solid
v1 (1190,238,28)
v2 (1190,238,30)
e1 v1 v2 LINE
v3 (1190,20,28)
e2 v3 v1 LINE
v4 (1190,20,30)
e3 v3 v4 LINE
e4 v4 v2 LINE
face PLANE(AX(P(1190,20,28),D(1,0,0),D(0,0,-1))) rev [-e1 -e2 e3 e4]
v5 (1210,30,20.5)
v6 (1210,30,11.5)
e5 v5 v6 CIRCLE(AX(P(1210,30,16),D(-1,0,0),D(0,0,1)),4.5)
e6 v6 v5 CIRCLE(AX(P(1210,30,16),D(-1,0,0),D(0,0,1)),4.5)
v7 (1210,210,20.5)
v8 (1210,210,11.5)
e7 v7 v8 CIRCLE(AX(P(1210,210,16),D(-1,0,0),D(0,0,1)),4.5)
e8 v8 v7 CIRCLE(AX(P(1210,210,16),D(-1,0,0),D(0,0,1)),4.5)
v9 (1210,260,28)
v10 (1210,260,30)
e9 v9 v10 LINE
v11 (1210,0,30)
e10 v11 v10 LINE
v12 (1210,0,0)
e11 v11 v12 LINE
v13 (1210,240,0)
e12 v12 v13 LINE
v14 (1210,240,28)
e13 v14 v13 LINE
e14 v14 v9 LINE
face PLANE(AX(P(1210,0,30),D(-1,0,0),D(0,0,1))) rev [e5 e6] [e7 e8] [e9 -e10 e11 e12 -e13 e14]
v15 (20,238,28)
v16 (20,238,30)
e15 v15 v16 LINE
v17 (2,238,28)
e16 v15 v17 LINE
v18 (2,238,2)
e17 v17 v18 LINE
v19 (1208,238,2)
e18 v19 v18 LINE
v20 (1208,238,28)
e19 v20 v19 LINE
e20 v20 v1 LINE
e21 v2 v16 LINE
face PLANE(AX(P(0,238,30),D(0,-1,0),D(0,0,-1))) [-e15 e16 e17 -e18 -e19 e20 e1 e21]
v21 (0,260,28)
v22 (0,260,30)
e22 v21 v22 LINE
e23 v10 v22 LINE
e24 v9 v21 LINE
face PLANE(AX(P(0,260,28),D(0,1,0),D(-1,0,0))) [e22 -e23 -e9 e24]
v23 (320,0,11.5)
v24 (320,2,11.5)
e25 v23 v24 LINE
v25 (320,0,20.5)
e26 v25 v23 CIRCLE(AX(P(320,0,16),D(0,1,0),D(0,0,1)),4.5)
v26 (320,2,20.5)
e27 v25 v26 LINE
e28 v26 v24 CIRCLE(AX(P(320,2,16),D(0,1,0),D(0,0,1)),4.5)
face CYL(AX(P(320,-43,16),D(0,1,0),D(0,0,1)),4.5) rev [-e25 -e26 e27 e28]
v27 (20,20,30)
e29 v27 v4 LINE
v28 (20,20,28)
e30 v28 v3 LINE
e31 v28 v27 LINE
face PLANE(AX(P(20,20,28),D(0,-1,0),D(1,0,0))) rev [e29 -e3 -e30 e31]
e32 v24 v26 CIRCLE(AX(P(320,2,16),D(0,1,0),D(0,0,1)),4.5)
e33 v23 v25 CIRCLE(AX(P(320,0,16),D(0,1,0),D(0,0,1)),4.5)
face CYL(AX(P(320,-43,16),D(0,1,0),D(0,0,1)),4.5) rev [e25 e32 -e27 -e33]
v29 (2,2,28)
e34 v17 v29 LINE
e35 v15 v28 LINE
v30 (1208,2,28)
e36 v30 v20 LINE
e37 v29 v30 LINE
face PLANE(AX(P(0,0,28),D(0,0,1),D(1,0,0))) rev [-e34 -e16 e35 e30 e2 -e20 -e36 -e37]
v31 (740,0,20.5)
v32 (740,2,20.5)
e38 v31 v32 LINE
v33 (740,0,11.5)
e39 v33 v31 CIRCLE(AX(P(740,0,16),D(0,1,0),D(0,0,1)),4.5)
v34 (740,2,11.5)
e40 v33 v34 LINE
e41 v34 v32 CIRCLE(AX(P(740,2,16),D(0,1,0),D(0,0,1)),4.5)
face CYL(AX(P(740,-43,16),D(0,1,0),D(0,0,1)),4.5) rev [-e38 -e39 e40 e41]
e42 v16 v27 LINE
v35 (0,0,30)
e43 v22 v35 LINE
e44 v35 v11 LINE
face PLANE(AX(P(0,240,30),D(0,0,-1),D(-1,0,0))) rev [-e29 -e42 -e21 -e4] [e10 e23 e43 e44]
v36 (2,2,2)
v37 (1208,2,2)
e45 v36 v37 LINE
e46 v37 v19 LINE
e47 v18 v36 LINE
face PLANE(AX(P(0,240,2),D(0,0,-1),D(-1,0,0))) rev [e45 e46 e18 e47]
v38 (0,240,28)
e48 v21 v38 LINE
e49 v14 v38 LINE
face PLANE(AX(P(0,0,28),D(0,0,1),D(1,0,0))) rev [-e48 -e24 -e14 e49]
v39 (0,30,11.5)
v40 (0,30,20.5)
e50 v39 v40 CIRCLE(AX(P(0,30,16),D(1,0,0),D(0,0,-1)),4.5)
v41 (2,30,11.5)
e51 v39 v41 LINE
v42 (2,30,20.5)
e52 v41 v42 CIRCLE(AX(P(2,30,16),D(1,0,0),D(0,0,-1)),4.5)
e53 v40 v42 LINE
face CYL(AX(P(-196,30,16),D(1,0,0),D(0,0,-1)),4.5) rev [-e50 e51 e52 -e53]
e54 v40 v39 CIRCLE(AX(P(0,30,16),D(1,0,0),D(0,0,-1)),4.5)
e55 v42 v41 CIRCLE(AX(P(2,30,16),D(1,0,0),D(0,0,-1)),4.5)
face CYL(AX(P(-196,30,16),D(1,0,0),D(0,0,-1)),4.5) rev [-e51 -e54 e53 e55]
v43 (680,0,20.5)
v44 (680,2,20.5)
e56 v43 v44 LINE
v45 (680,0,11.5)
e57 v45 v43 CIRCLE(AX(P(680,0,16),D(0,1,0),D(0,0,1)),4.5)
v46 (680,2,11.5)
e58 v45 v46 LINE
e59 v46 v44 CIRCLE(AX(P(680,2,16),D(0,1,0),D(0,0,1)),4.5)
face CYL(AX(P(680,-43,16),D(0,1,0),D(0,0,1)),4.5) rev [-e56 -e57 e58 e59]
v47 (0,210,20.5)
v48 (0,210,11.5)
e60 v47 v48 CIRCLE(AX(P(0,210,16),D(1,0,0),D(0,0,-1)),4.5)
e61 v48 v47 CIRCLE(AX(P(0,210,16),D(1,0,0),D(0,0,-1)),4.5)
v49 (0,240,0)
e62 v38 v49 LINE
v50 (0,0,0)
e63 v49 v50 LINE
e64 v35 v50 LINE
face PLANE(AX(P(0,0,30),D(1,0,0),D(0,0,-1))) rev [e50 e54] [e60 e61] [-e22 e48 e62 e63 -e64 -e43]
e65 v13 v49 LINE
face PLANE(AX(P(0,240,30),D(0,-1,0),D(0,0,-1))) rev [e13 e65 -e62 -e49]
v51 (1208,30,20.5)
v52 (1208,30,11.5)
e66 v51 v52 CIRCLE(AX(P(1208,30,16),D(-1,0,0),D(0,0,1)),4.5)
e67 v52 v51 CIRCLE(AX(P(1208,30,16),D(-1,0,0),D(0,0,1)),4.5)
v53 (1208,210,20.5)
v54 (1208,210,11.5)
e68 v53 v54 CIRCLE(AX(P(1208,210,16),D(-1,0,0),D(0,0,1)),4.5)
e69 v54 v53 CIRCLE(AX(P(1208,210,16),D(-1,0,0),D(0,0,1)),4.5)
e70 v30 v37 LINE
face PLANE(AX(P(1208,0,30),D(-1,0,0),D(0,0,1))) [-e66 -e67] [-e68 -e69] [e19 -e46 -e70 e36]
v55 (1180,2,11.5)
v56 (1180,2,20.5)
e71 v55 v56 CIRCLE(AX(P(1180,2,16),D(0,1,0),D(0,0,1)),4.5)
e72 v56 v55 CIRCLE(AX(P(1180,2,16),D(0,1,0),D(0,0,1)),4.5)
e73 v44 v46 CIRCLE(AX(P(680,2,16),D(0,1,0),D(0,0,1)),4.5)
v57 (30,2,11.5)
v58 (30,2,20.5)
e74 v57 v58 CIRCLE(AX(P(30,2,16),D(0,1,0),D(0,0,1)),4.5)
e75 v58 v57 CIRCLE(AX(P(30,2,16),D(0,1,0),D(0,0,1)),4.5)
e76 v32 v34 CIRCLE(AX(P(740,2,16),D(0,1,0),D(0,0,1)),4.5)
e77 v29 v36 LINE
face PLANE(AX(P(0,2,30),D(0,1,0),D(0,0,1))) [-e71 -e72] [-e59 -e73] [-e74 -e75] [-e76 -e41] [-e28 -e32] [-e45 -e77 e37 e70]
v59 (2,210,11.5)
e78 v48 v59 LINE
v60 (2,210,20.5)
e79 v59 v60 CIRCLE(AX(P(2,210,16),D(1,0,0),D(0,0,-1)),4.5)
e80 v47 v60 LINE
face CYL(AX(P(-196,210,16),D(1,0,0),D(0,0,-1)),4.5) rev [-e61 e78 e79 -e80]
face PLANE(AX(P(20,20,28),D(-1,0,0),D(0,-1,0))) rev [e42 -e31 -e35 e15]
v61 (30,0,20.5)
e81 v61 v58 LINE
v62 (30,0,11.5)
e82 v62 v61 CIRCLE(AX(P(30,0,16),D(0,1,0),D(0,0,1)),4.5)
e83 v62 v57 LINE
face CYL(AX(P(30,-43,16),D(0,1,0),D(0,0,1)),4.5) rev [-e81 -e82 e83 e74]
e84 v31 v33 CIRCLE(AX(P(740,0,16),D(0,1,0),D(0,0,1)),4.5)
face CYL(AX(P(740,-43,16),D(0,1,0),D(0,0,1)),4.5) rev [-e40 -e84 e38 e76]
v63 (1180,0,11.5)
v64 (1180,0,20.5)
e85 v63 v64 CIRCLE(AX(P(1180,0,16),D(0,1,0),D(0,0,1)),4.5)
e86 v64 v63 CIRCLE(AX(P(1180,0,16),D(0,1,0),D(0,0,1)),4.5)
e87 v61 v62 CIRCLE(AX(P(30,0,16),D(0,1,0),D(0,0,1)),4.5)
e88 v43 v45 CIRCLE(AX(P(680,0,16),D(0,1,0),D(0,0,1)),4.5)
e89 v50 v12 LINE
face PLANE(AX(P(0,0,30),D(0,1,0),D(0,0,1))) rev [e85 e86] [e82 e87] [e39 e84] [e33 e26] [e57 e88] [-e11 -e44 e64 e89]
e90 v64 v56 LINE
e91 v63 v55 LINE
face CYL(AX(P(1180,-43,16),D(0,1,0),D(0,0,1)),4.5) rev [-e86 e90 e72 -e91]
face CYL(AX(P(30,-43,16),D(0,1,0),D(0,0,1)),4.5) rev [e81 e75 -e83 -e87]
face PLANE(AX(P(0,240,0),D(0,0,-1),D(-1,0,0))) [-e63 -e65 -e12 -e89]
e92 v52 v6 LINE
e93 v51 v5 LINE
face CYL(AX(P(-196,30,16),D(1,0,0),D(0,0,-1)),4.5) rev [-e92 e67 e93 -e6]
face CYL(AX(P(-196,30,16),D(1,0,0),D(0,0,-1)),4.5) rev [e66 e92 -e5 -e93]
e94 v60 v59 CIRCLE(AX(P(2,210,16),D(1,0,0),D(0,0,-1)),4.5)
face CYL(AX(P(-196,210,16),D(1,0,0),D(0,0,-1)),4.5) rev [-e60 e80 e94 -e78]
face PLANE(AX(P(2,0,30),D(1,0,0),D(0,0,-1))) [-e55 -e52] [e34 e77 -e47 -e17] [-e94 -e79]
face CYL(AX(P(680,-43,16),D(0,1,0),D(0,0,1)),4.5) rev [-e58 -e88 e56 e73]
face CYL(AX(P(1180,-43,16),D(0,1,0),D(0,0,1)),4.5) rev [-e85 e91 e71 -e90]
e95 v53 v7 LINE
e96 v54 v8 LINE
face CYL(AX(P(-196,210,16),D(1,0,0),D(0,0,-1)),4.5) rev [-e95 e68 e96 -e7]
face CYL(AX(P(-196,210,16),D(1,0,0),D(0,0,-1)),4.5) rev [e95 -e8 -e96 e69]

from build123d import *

# Parameters (mm, degrees)
SKETCH_1_W               = 1210
SKETCH_1_H               = 240
EXTRUDE_1_DEPTH          = 30
SHELL_1_T                = -2
SKETCH_2_W               = 1210
SKETCH_2_H               = 260
SKETCH_2_W_2             = 1170
SKETCH_2_H_2             = 218
EXTRUDE_2_DEPTH          = 2
CUT_EXTRUDE_1_DEPTH      = 1316
CUT_EXTRUDE_1_DEPTH_BACK = 198
SKETCH_3_R               = 4.5
SKETCH_4_R               = 4.5
CUT_EXTRUDE_2_DEPTH      = 45


with BuildPart() as part:
    # 草图1 → 凸台-拉伸1 (new body)
    with BuildSketch(Plane.XY):
        with Locations((605, 120)):
            Rectangle(SKETCH_1_W, SKETCH_1_H)
    extrude(amount=EXTRUDE_1_DEPTH)

    # 抽壳1
    shell_1_openings = [part.faces().sort_by_distance(p)[0] for p in [
        (605, 120, 30),
    ]]
    offset(amount=SHELL_1_T, openings=shell_1_openings, kind=Kind.INTERSECTION)

    # 草图2 → 凸台-拉伸2 (add)
    with BuildSketch(Plane.XY.offset(30)):
        with Locations((605, 130)):
            Rectangle(SKETCH_2_W, SKETCH_2_H)
        with Locations((605, 129)):
            Rectangle(SKETCH_2_W_2, SKETCH_2_H_2, mode=Mode.SUBTRACT)
    extrude(amount=-EXTRUDE_2_DEPTH)

    # 草图3 → 切除-拉伸1 (cut, two sides: drawn at the far end of the back side and taken through both)
    with BuildSketch(Plane(origin=(2, 0, 0), x_dir=(0, 0, -1), z_dir=(1, 0, 0)).offset(-CUT_EXTRUDE_1_DEPTH_BACK)):
        with Locations(Location((-16, 30, 0), (0, 0, 180))):
            Circle(SKETCH_3_R)
        with Locations(Location((-16, 210, 0), (0, 0, 180))):
            Circle(SKETCH_3_R)
    extrude(amount=CUT_EXTRUDE_1_DEPTH + CUT_EXTRUDE_1_DEPTH_BACK, mode=Mode.SUBTRACT)

    # 草图4 → 切除-拉伸2 (cut)
    with BuildSketch(Plane(origin=(0, 2, 0), x_dir=(1, 0, 0), z_dir=(0, 1, 0))):
        with Locations(Location((30, -16, 0), (0, 0, 270))):
            Circle(SKETCH_4_R)
        with Locations(Location((1180, -16, 0), (0, 0, 270))):
            Circle(SKETCH_4_R)
        with Locations(Location((680, -16, 0), (0, 0, 270))):
            Circle(SKETCH_4_R)
        with Locations(Location((320, -16, 0), (0, 0, 270))):
            Circle(SKETCH_4_R)
        with Locations(Location((740, -16, 0), (0, 0, 270))):
            Circle(SKETCH_4_R)
    extrude(amount=-CUT_EXTRUDE_2_DEPTH, mode=Mode.SUBTRACT)


solid = part.part
